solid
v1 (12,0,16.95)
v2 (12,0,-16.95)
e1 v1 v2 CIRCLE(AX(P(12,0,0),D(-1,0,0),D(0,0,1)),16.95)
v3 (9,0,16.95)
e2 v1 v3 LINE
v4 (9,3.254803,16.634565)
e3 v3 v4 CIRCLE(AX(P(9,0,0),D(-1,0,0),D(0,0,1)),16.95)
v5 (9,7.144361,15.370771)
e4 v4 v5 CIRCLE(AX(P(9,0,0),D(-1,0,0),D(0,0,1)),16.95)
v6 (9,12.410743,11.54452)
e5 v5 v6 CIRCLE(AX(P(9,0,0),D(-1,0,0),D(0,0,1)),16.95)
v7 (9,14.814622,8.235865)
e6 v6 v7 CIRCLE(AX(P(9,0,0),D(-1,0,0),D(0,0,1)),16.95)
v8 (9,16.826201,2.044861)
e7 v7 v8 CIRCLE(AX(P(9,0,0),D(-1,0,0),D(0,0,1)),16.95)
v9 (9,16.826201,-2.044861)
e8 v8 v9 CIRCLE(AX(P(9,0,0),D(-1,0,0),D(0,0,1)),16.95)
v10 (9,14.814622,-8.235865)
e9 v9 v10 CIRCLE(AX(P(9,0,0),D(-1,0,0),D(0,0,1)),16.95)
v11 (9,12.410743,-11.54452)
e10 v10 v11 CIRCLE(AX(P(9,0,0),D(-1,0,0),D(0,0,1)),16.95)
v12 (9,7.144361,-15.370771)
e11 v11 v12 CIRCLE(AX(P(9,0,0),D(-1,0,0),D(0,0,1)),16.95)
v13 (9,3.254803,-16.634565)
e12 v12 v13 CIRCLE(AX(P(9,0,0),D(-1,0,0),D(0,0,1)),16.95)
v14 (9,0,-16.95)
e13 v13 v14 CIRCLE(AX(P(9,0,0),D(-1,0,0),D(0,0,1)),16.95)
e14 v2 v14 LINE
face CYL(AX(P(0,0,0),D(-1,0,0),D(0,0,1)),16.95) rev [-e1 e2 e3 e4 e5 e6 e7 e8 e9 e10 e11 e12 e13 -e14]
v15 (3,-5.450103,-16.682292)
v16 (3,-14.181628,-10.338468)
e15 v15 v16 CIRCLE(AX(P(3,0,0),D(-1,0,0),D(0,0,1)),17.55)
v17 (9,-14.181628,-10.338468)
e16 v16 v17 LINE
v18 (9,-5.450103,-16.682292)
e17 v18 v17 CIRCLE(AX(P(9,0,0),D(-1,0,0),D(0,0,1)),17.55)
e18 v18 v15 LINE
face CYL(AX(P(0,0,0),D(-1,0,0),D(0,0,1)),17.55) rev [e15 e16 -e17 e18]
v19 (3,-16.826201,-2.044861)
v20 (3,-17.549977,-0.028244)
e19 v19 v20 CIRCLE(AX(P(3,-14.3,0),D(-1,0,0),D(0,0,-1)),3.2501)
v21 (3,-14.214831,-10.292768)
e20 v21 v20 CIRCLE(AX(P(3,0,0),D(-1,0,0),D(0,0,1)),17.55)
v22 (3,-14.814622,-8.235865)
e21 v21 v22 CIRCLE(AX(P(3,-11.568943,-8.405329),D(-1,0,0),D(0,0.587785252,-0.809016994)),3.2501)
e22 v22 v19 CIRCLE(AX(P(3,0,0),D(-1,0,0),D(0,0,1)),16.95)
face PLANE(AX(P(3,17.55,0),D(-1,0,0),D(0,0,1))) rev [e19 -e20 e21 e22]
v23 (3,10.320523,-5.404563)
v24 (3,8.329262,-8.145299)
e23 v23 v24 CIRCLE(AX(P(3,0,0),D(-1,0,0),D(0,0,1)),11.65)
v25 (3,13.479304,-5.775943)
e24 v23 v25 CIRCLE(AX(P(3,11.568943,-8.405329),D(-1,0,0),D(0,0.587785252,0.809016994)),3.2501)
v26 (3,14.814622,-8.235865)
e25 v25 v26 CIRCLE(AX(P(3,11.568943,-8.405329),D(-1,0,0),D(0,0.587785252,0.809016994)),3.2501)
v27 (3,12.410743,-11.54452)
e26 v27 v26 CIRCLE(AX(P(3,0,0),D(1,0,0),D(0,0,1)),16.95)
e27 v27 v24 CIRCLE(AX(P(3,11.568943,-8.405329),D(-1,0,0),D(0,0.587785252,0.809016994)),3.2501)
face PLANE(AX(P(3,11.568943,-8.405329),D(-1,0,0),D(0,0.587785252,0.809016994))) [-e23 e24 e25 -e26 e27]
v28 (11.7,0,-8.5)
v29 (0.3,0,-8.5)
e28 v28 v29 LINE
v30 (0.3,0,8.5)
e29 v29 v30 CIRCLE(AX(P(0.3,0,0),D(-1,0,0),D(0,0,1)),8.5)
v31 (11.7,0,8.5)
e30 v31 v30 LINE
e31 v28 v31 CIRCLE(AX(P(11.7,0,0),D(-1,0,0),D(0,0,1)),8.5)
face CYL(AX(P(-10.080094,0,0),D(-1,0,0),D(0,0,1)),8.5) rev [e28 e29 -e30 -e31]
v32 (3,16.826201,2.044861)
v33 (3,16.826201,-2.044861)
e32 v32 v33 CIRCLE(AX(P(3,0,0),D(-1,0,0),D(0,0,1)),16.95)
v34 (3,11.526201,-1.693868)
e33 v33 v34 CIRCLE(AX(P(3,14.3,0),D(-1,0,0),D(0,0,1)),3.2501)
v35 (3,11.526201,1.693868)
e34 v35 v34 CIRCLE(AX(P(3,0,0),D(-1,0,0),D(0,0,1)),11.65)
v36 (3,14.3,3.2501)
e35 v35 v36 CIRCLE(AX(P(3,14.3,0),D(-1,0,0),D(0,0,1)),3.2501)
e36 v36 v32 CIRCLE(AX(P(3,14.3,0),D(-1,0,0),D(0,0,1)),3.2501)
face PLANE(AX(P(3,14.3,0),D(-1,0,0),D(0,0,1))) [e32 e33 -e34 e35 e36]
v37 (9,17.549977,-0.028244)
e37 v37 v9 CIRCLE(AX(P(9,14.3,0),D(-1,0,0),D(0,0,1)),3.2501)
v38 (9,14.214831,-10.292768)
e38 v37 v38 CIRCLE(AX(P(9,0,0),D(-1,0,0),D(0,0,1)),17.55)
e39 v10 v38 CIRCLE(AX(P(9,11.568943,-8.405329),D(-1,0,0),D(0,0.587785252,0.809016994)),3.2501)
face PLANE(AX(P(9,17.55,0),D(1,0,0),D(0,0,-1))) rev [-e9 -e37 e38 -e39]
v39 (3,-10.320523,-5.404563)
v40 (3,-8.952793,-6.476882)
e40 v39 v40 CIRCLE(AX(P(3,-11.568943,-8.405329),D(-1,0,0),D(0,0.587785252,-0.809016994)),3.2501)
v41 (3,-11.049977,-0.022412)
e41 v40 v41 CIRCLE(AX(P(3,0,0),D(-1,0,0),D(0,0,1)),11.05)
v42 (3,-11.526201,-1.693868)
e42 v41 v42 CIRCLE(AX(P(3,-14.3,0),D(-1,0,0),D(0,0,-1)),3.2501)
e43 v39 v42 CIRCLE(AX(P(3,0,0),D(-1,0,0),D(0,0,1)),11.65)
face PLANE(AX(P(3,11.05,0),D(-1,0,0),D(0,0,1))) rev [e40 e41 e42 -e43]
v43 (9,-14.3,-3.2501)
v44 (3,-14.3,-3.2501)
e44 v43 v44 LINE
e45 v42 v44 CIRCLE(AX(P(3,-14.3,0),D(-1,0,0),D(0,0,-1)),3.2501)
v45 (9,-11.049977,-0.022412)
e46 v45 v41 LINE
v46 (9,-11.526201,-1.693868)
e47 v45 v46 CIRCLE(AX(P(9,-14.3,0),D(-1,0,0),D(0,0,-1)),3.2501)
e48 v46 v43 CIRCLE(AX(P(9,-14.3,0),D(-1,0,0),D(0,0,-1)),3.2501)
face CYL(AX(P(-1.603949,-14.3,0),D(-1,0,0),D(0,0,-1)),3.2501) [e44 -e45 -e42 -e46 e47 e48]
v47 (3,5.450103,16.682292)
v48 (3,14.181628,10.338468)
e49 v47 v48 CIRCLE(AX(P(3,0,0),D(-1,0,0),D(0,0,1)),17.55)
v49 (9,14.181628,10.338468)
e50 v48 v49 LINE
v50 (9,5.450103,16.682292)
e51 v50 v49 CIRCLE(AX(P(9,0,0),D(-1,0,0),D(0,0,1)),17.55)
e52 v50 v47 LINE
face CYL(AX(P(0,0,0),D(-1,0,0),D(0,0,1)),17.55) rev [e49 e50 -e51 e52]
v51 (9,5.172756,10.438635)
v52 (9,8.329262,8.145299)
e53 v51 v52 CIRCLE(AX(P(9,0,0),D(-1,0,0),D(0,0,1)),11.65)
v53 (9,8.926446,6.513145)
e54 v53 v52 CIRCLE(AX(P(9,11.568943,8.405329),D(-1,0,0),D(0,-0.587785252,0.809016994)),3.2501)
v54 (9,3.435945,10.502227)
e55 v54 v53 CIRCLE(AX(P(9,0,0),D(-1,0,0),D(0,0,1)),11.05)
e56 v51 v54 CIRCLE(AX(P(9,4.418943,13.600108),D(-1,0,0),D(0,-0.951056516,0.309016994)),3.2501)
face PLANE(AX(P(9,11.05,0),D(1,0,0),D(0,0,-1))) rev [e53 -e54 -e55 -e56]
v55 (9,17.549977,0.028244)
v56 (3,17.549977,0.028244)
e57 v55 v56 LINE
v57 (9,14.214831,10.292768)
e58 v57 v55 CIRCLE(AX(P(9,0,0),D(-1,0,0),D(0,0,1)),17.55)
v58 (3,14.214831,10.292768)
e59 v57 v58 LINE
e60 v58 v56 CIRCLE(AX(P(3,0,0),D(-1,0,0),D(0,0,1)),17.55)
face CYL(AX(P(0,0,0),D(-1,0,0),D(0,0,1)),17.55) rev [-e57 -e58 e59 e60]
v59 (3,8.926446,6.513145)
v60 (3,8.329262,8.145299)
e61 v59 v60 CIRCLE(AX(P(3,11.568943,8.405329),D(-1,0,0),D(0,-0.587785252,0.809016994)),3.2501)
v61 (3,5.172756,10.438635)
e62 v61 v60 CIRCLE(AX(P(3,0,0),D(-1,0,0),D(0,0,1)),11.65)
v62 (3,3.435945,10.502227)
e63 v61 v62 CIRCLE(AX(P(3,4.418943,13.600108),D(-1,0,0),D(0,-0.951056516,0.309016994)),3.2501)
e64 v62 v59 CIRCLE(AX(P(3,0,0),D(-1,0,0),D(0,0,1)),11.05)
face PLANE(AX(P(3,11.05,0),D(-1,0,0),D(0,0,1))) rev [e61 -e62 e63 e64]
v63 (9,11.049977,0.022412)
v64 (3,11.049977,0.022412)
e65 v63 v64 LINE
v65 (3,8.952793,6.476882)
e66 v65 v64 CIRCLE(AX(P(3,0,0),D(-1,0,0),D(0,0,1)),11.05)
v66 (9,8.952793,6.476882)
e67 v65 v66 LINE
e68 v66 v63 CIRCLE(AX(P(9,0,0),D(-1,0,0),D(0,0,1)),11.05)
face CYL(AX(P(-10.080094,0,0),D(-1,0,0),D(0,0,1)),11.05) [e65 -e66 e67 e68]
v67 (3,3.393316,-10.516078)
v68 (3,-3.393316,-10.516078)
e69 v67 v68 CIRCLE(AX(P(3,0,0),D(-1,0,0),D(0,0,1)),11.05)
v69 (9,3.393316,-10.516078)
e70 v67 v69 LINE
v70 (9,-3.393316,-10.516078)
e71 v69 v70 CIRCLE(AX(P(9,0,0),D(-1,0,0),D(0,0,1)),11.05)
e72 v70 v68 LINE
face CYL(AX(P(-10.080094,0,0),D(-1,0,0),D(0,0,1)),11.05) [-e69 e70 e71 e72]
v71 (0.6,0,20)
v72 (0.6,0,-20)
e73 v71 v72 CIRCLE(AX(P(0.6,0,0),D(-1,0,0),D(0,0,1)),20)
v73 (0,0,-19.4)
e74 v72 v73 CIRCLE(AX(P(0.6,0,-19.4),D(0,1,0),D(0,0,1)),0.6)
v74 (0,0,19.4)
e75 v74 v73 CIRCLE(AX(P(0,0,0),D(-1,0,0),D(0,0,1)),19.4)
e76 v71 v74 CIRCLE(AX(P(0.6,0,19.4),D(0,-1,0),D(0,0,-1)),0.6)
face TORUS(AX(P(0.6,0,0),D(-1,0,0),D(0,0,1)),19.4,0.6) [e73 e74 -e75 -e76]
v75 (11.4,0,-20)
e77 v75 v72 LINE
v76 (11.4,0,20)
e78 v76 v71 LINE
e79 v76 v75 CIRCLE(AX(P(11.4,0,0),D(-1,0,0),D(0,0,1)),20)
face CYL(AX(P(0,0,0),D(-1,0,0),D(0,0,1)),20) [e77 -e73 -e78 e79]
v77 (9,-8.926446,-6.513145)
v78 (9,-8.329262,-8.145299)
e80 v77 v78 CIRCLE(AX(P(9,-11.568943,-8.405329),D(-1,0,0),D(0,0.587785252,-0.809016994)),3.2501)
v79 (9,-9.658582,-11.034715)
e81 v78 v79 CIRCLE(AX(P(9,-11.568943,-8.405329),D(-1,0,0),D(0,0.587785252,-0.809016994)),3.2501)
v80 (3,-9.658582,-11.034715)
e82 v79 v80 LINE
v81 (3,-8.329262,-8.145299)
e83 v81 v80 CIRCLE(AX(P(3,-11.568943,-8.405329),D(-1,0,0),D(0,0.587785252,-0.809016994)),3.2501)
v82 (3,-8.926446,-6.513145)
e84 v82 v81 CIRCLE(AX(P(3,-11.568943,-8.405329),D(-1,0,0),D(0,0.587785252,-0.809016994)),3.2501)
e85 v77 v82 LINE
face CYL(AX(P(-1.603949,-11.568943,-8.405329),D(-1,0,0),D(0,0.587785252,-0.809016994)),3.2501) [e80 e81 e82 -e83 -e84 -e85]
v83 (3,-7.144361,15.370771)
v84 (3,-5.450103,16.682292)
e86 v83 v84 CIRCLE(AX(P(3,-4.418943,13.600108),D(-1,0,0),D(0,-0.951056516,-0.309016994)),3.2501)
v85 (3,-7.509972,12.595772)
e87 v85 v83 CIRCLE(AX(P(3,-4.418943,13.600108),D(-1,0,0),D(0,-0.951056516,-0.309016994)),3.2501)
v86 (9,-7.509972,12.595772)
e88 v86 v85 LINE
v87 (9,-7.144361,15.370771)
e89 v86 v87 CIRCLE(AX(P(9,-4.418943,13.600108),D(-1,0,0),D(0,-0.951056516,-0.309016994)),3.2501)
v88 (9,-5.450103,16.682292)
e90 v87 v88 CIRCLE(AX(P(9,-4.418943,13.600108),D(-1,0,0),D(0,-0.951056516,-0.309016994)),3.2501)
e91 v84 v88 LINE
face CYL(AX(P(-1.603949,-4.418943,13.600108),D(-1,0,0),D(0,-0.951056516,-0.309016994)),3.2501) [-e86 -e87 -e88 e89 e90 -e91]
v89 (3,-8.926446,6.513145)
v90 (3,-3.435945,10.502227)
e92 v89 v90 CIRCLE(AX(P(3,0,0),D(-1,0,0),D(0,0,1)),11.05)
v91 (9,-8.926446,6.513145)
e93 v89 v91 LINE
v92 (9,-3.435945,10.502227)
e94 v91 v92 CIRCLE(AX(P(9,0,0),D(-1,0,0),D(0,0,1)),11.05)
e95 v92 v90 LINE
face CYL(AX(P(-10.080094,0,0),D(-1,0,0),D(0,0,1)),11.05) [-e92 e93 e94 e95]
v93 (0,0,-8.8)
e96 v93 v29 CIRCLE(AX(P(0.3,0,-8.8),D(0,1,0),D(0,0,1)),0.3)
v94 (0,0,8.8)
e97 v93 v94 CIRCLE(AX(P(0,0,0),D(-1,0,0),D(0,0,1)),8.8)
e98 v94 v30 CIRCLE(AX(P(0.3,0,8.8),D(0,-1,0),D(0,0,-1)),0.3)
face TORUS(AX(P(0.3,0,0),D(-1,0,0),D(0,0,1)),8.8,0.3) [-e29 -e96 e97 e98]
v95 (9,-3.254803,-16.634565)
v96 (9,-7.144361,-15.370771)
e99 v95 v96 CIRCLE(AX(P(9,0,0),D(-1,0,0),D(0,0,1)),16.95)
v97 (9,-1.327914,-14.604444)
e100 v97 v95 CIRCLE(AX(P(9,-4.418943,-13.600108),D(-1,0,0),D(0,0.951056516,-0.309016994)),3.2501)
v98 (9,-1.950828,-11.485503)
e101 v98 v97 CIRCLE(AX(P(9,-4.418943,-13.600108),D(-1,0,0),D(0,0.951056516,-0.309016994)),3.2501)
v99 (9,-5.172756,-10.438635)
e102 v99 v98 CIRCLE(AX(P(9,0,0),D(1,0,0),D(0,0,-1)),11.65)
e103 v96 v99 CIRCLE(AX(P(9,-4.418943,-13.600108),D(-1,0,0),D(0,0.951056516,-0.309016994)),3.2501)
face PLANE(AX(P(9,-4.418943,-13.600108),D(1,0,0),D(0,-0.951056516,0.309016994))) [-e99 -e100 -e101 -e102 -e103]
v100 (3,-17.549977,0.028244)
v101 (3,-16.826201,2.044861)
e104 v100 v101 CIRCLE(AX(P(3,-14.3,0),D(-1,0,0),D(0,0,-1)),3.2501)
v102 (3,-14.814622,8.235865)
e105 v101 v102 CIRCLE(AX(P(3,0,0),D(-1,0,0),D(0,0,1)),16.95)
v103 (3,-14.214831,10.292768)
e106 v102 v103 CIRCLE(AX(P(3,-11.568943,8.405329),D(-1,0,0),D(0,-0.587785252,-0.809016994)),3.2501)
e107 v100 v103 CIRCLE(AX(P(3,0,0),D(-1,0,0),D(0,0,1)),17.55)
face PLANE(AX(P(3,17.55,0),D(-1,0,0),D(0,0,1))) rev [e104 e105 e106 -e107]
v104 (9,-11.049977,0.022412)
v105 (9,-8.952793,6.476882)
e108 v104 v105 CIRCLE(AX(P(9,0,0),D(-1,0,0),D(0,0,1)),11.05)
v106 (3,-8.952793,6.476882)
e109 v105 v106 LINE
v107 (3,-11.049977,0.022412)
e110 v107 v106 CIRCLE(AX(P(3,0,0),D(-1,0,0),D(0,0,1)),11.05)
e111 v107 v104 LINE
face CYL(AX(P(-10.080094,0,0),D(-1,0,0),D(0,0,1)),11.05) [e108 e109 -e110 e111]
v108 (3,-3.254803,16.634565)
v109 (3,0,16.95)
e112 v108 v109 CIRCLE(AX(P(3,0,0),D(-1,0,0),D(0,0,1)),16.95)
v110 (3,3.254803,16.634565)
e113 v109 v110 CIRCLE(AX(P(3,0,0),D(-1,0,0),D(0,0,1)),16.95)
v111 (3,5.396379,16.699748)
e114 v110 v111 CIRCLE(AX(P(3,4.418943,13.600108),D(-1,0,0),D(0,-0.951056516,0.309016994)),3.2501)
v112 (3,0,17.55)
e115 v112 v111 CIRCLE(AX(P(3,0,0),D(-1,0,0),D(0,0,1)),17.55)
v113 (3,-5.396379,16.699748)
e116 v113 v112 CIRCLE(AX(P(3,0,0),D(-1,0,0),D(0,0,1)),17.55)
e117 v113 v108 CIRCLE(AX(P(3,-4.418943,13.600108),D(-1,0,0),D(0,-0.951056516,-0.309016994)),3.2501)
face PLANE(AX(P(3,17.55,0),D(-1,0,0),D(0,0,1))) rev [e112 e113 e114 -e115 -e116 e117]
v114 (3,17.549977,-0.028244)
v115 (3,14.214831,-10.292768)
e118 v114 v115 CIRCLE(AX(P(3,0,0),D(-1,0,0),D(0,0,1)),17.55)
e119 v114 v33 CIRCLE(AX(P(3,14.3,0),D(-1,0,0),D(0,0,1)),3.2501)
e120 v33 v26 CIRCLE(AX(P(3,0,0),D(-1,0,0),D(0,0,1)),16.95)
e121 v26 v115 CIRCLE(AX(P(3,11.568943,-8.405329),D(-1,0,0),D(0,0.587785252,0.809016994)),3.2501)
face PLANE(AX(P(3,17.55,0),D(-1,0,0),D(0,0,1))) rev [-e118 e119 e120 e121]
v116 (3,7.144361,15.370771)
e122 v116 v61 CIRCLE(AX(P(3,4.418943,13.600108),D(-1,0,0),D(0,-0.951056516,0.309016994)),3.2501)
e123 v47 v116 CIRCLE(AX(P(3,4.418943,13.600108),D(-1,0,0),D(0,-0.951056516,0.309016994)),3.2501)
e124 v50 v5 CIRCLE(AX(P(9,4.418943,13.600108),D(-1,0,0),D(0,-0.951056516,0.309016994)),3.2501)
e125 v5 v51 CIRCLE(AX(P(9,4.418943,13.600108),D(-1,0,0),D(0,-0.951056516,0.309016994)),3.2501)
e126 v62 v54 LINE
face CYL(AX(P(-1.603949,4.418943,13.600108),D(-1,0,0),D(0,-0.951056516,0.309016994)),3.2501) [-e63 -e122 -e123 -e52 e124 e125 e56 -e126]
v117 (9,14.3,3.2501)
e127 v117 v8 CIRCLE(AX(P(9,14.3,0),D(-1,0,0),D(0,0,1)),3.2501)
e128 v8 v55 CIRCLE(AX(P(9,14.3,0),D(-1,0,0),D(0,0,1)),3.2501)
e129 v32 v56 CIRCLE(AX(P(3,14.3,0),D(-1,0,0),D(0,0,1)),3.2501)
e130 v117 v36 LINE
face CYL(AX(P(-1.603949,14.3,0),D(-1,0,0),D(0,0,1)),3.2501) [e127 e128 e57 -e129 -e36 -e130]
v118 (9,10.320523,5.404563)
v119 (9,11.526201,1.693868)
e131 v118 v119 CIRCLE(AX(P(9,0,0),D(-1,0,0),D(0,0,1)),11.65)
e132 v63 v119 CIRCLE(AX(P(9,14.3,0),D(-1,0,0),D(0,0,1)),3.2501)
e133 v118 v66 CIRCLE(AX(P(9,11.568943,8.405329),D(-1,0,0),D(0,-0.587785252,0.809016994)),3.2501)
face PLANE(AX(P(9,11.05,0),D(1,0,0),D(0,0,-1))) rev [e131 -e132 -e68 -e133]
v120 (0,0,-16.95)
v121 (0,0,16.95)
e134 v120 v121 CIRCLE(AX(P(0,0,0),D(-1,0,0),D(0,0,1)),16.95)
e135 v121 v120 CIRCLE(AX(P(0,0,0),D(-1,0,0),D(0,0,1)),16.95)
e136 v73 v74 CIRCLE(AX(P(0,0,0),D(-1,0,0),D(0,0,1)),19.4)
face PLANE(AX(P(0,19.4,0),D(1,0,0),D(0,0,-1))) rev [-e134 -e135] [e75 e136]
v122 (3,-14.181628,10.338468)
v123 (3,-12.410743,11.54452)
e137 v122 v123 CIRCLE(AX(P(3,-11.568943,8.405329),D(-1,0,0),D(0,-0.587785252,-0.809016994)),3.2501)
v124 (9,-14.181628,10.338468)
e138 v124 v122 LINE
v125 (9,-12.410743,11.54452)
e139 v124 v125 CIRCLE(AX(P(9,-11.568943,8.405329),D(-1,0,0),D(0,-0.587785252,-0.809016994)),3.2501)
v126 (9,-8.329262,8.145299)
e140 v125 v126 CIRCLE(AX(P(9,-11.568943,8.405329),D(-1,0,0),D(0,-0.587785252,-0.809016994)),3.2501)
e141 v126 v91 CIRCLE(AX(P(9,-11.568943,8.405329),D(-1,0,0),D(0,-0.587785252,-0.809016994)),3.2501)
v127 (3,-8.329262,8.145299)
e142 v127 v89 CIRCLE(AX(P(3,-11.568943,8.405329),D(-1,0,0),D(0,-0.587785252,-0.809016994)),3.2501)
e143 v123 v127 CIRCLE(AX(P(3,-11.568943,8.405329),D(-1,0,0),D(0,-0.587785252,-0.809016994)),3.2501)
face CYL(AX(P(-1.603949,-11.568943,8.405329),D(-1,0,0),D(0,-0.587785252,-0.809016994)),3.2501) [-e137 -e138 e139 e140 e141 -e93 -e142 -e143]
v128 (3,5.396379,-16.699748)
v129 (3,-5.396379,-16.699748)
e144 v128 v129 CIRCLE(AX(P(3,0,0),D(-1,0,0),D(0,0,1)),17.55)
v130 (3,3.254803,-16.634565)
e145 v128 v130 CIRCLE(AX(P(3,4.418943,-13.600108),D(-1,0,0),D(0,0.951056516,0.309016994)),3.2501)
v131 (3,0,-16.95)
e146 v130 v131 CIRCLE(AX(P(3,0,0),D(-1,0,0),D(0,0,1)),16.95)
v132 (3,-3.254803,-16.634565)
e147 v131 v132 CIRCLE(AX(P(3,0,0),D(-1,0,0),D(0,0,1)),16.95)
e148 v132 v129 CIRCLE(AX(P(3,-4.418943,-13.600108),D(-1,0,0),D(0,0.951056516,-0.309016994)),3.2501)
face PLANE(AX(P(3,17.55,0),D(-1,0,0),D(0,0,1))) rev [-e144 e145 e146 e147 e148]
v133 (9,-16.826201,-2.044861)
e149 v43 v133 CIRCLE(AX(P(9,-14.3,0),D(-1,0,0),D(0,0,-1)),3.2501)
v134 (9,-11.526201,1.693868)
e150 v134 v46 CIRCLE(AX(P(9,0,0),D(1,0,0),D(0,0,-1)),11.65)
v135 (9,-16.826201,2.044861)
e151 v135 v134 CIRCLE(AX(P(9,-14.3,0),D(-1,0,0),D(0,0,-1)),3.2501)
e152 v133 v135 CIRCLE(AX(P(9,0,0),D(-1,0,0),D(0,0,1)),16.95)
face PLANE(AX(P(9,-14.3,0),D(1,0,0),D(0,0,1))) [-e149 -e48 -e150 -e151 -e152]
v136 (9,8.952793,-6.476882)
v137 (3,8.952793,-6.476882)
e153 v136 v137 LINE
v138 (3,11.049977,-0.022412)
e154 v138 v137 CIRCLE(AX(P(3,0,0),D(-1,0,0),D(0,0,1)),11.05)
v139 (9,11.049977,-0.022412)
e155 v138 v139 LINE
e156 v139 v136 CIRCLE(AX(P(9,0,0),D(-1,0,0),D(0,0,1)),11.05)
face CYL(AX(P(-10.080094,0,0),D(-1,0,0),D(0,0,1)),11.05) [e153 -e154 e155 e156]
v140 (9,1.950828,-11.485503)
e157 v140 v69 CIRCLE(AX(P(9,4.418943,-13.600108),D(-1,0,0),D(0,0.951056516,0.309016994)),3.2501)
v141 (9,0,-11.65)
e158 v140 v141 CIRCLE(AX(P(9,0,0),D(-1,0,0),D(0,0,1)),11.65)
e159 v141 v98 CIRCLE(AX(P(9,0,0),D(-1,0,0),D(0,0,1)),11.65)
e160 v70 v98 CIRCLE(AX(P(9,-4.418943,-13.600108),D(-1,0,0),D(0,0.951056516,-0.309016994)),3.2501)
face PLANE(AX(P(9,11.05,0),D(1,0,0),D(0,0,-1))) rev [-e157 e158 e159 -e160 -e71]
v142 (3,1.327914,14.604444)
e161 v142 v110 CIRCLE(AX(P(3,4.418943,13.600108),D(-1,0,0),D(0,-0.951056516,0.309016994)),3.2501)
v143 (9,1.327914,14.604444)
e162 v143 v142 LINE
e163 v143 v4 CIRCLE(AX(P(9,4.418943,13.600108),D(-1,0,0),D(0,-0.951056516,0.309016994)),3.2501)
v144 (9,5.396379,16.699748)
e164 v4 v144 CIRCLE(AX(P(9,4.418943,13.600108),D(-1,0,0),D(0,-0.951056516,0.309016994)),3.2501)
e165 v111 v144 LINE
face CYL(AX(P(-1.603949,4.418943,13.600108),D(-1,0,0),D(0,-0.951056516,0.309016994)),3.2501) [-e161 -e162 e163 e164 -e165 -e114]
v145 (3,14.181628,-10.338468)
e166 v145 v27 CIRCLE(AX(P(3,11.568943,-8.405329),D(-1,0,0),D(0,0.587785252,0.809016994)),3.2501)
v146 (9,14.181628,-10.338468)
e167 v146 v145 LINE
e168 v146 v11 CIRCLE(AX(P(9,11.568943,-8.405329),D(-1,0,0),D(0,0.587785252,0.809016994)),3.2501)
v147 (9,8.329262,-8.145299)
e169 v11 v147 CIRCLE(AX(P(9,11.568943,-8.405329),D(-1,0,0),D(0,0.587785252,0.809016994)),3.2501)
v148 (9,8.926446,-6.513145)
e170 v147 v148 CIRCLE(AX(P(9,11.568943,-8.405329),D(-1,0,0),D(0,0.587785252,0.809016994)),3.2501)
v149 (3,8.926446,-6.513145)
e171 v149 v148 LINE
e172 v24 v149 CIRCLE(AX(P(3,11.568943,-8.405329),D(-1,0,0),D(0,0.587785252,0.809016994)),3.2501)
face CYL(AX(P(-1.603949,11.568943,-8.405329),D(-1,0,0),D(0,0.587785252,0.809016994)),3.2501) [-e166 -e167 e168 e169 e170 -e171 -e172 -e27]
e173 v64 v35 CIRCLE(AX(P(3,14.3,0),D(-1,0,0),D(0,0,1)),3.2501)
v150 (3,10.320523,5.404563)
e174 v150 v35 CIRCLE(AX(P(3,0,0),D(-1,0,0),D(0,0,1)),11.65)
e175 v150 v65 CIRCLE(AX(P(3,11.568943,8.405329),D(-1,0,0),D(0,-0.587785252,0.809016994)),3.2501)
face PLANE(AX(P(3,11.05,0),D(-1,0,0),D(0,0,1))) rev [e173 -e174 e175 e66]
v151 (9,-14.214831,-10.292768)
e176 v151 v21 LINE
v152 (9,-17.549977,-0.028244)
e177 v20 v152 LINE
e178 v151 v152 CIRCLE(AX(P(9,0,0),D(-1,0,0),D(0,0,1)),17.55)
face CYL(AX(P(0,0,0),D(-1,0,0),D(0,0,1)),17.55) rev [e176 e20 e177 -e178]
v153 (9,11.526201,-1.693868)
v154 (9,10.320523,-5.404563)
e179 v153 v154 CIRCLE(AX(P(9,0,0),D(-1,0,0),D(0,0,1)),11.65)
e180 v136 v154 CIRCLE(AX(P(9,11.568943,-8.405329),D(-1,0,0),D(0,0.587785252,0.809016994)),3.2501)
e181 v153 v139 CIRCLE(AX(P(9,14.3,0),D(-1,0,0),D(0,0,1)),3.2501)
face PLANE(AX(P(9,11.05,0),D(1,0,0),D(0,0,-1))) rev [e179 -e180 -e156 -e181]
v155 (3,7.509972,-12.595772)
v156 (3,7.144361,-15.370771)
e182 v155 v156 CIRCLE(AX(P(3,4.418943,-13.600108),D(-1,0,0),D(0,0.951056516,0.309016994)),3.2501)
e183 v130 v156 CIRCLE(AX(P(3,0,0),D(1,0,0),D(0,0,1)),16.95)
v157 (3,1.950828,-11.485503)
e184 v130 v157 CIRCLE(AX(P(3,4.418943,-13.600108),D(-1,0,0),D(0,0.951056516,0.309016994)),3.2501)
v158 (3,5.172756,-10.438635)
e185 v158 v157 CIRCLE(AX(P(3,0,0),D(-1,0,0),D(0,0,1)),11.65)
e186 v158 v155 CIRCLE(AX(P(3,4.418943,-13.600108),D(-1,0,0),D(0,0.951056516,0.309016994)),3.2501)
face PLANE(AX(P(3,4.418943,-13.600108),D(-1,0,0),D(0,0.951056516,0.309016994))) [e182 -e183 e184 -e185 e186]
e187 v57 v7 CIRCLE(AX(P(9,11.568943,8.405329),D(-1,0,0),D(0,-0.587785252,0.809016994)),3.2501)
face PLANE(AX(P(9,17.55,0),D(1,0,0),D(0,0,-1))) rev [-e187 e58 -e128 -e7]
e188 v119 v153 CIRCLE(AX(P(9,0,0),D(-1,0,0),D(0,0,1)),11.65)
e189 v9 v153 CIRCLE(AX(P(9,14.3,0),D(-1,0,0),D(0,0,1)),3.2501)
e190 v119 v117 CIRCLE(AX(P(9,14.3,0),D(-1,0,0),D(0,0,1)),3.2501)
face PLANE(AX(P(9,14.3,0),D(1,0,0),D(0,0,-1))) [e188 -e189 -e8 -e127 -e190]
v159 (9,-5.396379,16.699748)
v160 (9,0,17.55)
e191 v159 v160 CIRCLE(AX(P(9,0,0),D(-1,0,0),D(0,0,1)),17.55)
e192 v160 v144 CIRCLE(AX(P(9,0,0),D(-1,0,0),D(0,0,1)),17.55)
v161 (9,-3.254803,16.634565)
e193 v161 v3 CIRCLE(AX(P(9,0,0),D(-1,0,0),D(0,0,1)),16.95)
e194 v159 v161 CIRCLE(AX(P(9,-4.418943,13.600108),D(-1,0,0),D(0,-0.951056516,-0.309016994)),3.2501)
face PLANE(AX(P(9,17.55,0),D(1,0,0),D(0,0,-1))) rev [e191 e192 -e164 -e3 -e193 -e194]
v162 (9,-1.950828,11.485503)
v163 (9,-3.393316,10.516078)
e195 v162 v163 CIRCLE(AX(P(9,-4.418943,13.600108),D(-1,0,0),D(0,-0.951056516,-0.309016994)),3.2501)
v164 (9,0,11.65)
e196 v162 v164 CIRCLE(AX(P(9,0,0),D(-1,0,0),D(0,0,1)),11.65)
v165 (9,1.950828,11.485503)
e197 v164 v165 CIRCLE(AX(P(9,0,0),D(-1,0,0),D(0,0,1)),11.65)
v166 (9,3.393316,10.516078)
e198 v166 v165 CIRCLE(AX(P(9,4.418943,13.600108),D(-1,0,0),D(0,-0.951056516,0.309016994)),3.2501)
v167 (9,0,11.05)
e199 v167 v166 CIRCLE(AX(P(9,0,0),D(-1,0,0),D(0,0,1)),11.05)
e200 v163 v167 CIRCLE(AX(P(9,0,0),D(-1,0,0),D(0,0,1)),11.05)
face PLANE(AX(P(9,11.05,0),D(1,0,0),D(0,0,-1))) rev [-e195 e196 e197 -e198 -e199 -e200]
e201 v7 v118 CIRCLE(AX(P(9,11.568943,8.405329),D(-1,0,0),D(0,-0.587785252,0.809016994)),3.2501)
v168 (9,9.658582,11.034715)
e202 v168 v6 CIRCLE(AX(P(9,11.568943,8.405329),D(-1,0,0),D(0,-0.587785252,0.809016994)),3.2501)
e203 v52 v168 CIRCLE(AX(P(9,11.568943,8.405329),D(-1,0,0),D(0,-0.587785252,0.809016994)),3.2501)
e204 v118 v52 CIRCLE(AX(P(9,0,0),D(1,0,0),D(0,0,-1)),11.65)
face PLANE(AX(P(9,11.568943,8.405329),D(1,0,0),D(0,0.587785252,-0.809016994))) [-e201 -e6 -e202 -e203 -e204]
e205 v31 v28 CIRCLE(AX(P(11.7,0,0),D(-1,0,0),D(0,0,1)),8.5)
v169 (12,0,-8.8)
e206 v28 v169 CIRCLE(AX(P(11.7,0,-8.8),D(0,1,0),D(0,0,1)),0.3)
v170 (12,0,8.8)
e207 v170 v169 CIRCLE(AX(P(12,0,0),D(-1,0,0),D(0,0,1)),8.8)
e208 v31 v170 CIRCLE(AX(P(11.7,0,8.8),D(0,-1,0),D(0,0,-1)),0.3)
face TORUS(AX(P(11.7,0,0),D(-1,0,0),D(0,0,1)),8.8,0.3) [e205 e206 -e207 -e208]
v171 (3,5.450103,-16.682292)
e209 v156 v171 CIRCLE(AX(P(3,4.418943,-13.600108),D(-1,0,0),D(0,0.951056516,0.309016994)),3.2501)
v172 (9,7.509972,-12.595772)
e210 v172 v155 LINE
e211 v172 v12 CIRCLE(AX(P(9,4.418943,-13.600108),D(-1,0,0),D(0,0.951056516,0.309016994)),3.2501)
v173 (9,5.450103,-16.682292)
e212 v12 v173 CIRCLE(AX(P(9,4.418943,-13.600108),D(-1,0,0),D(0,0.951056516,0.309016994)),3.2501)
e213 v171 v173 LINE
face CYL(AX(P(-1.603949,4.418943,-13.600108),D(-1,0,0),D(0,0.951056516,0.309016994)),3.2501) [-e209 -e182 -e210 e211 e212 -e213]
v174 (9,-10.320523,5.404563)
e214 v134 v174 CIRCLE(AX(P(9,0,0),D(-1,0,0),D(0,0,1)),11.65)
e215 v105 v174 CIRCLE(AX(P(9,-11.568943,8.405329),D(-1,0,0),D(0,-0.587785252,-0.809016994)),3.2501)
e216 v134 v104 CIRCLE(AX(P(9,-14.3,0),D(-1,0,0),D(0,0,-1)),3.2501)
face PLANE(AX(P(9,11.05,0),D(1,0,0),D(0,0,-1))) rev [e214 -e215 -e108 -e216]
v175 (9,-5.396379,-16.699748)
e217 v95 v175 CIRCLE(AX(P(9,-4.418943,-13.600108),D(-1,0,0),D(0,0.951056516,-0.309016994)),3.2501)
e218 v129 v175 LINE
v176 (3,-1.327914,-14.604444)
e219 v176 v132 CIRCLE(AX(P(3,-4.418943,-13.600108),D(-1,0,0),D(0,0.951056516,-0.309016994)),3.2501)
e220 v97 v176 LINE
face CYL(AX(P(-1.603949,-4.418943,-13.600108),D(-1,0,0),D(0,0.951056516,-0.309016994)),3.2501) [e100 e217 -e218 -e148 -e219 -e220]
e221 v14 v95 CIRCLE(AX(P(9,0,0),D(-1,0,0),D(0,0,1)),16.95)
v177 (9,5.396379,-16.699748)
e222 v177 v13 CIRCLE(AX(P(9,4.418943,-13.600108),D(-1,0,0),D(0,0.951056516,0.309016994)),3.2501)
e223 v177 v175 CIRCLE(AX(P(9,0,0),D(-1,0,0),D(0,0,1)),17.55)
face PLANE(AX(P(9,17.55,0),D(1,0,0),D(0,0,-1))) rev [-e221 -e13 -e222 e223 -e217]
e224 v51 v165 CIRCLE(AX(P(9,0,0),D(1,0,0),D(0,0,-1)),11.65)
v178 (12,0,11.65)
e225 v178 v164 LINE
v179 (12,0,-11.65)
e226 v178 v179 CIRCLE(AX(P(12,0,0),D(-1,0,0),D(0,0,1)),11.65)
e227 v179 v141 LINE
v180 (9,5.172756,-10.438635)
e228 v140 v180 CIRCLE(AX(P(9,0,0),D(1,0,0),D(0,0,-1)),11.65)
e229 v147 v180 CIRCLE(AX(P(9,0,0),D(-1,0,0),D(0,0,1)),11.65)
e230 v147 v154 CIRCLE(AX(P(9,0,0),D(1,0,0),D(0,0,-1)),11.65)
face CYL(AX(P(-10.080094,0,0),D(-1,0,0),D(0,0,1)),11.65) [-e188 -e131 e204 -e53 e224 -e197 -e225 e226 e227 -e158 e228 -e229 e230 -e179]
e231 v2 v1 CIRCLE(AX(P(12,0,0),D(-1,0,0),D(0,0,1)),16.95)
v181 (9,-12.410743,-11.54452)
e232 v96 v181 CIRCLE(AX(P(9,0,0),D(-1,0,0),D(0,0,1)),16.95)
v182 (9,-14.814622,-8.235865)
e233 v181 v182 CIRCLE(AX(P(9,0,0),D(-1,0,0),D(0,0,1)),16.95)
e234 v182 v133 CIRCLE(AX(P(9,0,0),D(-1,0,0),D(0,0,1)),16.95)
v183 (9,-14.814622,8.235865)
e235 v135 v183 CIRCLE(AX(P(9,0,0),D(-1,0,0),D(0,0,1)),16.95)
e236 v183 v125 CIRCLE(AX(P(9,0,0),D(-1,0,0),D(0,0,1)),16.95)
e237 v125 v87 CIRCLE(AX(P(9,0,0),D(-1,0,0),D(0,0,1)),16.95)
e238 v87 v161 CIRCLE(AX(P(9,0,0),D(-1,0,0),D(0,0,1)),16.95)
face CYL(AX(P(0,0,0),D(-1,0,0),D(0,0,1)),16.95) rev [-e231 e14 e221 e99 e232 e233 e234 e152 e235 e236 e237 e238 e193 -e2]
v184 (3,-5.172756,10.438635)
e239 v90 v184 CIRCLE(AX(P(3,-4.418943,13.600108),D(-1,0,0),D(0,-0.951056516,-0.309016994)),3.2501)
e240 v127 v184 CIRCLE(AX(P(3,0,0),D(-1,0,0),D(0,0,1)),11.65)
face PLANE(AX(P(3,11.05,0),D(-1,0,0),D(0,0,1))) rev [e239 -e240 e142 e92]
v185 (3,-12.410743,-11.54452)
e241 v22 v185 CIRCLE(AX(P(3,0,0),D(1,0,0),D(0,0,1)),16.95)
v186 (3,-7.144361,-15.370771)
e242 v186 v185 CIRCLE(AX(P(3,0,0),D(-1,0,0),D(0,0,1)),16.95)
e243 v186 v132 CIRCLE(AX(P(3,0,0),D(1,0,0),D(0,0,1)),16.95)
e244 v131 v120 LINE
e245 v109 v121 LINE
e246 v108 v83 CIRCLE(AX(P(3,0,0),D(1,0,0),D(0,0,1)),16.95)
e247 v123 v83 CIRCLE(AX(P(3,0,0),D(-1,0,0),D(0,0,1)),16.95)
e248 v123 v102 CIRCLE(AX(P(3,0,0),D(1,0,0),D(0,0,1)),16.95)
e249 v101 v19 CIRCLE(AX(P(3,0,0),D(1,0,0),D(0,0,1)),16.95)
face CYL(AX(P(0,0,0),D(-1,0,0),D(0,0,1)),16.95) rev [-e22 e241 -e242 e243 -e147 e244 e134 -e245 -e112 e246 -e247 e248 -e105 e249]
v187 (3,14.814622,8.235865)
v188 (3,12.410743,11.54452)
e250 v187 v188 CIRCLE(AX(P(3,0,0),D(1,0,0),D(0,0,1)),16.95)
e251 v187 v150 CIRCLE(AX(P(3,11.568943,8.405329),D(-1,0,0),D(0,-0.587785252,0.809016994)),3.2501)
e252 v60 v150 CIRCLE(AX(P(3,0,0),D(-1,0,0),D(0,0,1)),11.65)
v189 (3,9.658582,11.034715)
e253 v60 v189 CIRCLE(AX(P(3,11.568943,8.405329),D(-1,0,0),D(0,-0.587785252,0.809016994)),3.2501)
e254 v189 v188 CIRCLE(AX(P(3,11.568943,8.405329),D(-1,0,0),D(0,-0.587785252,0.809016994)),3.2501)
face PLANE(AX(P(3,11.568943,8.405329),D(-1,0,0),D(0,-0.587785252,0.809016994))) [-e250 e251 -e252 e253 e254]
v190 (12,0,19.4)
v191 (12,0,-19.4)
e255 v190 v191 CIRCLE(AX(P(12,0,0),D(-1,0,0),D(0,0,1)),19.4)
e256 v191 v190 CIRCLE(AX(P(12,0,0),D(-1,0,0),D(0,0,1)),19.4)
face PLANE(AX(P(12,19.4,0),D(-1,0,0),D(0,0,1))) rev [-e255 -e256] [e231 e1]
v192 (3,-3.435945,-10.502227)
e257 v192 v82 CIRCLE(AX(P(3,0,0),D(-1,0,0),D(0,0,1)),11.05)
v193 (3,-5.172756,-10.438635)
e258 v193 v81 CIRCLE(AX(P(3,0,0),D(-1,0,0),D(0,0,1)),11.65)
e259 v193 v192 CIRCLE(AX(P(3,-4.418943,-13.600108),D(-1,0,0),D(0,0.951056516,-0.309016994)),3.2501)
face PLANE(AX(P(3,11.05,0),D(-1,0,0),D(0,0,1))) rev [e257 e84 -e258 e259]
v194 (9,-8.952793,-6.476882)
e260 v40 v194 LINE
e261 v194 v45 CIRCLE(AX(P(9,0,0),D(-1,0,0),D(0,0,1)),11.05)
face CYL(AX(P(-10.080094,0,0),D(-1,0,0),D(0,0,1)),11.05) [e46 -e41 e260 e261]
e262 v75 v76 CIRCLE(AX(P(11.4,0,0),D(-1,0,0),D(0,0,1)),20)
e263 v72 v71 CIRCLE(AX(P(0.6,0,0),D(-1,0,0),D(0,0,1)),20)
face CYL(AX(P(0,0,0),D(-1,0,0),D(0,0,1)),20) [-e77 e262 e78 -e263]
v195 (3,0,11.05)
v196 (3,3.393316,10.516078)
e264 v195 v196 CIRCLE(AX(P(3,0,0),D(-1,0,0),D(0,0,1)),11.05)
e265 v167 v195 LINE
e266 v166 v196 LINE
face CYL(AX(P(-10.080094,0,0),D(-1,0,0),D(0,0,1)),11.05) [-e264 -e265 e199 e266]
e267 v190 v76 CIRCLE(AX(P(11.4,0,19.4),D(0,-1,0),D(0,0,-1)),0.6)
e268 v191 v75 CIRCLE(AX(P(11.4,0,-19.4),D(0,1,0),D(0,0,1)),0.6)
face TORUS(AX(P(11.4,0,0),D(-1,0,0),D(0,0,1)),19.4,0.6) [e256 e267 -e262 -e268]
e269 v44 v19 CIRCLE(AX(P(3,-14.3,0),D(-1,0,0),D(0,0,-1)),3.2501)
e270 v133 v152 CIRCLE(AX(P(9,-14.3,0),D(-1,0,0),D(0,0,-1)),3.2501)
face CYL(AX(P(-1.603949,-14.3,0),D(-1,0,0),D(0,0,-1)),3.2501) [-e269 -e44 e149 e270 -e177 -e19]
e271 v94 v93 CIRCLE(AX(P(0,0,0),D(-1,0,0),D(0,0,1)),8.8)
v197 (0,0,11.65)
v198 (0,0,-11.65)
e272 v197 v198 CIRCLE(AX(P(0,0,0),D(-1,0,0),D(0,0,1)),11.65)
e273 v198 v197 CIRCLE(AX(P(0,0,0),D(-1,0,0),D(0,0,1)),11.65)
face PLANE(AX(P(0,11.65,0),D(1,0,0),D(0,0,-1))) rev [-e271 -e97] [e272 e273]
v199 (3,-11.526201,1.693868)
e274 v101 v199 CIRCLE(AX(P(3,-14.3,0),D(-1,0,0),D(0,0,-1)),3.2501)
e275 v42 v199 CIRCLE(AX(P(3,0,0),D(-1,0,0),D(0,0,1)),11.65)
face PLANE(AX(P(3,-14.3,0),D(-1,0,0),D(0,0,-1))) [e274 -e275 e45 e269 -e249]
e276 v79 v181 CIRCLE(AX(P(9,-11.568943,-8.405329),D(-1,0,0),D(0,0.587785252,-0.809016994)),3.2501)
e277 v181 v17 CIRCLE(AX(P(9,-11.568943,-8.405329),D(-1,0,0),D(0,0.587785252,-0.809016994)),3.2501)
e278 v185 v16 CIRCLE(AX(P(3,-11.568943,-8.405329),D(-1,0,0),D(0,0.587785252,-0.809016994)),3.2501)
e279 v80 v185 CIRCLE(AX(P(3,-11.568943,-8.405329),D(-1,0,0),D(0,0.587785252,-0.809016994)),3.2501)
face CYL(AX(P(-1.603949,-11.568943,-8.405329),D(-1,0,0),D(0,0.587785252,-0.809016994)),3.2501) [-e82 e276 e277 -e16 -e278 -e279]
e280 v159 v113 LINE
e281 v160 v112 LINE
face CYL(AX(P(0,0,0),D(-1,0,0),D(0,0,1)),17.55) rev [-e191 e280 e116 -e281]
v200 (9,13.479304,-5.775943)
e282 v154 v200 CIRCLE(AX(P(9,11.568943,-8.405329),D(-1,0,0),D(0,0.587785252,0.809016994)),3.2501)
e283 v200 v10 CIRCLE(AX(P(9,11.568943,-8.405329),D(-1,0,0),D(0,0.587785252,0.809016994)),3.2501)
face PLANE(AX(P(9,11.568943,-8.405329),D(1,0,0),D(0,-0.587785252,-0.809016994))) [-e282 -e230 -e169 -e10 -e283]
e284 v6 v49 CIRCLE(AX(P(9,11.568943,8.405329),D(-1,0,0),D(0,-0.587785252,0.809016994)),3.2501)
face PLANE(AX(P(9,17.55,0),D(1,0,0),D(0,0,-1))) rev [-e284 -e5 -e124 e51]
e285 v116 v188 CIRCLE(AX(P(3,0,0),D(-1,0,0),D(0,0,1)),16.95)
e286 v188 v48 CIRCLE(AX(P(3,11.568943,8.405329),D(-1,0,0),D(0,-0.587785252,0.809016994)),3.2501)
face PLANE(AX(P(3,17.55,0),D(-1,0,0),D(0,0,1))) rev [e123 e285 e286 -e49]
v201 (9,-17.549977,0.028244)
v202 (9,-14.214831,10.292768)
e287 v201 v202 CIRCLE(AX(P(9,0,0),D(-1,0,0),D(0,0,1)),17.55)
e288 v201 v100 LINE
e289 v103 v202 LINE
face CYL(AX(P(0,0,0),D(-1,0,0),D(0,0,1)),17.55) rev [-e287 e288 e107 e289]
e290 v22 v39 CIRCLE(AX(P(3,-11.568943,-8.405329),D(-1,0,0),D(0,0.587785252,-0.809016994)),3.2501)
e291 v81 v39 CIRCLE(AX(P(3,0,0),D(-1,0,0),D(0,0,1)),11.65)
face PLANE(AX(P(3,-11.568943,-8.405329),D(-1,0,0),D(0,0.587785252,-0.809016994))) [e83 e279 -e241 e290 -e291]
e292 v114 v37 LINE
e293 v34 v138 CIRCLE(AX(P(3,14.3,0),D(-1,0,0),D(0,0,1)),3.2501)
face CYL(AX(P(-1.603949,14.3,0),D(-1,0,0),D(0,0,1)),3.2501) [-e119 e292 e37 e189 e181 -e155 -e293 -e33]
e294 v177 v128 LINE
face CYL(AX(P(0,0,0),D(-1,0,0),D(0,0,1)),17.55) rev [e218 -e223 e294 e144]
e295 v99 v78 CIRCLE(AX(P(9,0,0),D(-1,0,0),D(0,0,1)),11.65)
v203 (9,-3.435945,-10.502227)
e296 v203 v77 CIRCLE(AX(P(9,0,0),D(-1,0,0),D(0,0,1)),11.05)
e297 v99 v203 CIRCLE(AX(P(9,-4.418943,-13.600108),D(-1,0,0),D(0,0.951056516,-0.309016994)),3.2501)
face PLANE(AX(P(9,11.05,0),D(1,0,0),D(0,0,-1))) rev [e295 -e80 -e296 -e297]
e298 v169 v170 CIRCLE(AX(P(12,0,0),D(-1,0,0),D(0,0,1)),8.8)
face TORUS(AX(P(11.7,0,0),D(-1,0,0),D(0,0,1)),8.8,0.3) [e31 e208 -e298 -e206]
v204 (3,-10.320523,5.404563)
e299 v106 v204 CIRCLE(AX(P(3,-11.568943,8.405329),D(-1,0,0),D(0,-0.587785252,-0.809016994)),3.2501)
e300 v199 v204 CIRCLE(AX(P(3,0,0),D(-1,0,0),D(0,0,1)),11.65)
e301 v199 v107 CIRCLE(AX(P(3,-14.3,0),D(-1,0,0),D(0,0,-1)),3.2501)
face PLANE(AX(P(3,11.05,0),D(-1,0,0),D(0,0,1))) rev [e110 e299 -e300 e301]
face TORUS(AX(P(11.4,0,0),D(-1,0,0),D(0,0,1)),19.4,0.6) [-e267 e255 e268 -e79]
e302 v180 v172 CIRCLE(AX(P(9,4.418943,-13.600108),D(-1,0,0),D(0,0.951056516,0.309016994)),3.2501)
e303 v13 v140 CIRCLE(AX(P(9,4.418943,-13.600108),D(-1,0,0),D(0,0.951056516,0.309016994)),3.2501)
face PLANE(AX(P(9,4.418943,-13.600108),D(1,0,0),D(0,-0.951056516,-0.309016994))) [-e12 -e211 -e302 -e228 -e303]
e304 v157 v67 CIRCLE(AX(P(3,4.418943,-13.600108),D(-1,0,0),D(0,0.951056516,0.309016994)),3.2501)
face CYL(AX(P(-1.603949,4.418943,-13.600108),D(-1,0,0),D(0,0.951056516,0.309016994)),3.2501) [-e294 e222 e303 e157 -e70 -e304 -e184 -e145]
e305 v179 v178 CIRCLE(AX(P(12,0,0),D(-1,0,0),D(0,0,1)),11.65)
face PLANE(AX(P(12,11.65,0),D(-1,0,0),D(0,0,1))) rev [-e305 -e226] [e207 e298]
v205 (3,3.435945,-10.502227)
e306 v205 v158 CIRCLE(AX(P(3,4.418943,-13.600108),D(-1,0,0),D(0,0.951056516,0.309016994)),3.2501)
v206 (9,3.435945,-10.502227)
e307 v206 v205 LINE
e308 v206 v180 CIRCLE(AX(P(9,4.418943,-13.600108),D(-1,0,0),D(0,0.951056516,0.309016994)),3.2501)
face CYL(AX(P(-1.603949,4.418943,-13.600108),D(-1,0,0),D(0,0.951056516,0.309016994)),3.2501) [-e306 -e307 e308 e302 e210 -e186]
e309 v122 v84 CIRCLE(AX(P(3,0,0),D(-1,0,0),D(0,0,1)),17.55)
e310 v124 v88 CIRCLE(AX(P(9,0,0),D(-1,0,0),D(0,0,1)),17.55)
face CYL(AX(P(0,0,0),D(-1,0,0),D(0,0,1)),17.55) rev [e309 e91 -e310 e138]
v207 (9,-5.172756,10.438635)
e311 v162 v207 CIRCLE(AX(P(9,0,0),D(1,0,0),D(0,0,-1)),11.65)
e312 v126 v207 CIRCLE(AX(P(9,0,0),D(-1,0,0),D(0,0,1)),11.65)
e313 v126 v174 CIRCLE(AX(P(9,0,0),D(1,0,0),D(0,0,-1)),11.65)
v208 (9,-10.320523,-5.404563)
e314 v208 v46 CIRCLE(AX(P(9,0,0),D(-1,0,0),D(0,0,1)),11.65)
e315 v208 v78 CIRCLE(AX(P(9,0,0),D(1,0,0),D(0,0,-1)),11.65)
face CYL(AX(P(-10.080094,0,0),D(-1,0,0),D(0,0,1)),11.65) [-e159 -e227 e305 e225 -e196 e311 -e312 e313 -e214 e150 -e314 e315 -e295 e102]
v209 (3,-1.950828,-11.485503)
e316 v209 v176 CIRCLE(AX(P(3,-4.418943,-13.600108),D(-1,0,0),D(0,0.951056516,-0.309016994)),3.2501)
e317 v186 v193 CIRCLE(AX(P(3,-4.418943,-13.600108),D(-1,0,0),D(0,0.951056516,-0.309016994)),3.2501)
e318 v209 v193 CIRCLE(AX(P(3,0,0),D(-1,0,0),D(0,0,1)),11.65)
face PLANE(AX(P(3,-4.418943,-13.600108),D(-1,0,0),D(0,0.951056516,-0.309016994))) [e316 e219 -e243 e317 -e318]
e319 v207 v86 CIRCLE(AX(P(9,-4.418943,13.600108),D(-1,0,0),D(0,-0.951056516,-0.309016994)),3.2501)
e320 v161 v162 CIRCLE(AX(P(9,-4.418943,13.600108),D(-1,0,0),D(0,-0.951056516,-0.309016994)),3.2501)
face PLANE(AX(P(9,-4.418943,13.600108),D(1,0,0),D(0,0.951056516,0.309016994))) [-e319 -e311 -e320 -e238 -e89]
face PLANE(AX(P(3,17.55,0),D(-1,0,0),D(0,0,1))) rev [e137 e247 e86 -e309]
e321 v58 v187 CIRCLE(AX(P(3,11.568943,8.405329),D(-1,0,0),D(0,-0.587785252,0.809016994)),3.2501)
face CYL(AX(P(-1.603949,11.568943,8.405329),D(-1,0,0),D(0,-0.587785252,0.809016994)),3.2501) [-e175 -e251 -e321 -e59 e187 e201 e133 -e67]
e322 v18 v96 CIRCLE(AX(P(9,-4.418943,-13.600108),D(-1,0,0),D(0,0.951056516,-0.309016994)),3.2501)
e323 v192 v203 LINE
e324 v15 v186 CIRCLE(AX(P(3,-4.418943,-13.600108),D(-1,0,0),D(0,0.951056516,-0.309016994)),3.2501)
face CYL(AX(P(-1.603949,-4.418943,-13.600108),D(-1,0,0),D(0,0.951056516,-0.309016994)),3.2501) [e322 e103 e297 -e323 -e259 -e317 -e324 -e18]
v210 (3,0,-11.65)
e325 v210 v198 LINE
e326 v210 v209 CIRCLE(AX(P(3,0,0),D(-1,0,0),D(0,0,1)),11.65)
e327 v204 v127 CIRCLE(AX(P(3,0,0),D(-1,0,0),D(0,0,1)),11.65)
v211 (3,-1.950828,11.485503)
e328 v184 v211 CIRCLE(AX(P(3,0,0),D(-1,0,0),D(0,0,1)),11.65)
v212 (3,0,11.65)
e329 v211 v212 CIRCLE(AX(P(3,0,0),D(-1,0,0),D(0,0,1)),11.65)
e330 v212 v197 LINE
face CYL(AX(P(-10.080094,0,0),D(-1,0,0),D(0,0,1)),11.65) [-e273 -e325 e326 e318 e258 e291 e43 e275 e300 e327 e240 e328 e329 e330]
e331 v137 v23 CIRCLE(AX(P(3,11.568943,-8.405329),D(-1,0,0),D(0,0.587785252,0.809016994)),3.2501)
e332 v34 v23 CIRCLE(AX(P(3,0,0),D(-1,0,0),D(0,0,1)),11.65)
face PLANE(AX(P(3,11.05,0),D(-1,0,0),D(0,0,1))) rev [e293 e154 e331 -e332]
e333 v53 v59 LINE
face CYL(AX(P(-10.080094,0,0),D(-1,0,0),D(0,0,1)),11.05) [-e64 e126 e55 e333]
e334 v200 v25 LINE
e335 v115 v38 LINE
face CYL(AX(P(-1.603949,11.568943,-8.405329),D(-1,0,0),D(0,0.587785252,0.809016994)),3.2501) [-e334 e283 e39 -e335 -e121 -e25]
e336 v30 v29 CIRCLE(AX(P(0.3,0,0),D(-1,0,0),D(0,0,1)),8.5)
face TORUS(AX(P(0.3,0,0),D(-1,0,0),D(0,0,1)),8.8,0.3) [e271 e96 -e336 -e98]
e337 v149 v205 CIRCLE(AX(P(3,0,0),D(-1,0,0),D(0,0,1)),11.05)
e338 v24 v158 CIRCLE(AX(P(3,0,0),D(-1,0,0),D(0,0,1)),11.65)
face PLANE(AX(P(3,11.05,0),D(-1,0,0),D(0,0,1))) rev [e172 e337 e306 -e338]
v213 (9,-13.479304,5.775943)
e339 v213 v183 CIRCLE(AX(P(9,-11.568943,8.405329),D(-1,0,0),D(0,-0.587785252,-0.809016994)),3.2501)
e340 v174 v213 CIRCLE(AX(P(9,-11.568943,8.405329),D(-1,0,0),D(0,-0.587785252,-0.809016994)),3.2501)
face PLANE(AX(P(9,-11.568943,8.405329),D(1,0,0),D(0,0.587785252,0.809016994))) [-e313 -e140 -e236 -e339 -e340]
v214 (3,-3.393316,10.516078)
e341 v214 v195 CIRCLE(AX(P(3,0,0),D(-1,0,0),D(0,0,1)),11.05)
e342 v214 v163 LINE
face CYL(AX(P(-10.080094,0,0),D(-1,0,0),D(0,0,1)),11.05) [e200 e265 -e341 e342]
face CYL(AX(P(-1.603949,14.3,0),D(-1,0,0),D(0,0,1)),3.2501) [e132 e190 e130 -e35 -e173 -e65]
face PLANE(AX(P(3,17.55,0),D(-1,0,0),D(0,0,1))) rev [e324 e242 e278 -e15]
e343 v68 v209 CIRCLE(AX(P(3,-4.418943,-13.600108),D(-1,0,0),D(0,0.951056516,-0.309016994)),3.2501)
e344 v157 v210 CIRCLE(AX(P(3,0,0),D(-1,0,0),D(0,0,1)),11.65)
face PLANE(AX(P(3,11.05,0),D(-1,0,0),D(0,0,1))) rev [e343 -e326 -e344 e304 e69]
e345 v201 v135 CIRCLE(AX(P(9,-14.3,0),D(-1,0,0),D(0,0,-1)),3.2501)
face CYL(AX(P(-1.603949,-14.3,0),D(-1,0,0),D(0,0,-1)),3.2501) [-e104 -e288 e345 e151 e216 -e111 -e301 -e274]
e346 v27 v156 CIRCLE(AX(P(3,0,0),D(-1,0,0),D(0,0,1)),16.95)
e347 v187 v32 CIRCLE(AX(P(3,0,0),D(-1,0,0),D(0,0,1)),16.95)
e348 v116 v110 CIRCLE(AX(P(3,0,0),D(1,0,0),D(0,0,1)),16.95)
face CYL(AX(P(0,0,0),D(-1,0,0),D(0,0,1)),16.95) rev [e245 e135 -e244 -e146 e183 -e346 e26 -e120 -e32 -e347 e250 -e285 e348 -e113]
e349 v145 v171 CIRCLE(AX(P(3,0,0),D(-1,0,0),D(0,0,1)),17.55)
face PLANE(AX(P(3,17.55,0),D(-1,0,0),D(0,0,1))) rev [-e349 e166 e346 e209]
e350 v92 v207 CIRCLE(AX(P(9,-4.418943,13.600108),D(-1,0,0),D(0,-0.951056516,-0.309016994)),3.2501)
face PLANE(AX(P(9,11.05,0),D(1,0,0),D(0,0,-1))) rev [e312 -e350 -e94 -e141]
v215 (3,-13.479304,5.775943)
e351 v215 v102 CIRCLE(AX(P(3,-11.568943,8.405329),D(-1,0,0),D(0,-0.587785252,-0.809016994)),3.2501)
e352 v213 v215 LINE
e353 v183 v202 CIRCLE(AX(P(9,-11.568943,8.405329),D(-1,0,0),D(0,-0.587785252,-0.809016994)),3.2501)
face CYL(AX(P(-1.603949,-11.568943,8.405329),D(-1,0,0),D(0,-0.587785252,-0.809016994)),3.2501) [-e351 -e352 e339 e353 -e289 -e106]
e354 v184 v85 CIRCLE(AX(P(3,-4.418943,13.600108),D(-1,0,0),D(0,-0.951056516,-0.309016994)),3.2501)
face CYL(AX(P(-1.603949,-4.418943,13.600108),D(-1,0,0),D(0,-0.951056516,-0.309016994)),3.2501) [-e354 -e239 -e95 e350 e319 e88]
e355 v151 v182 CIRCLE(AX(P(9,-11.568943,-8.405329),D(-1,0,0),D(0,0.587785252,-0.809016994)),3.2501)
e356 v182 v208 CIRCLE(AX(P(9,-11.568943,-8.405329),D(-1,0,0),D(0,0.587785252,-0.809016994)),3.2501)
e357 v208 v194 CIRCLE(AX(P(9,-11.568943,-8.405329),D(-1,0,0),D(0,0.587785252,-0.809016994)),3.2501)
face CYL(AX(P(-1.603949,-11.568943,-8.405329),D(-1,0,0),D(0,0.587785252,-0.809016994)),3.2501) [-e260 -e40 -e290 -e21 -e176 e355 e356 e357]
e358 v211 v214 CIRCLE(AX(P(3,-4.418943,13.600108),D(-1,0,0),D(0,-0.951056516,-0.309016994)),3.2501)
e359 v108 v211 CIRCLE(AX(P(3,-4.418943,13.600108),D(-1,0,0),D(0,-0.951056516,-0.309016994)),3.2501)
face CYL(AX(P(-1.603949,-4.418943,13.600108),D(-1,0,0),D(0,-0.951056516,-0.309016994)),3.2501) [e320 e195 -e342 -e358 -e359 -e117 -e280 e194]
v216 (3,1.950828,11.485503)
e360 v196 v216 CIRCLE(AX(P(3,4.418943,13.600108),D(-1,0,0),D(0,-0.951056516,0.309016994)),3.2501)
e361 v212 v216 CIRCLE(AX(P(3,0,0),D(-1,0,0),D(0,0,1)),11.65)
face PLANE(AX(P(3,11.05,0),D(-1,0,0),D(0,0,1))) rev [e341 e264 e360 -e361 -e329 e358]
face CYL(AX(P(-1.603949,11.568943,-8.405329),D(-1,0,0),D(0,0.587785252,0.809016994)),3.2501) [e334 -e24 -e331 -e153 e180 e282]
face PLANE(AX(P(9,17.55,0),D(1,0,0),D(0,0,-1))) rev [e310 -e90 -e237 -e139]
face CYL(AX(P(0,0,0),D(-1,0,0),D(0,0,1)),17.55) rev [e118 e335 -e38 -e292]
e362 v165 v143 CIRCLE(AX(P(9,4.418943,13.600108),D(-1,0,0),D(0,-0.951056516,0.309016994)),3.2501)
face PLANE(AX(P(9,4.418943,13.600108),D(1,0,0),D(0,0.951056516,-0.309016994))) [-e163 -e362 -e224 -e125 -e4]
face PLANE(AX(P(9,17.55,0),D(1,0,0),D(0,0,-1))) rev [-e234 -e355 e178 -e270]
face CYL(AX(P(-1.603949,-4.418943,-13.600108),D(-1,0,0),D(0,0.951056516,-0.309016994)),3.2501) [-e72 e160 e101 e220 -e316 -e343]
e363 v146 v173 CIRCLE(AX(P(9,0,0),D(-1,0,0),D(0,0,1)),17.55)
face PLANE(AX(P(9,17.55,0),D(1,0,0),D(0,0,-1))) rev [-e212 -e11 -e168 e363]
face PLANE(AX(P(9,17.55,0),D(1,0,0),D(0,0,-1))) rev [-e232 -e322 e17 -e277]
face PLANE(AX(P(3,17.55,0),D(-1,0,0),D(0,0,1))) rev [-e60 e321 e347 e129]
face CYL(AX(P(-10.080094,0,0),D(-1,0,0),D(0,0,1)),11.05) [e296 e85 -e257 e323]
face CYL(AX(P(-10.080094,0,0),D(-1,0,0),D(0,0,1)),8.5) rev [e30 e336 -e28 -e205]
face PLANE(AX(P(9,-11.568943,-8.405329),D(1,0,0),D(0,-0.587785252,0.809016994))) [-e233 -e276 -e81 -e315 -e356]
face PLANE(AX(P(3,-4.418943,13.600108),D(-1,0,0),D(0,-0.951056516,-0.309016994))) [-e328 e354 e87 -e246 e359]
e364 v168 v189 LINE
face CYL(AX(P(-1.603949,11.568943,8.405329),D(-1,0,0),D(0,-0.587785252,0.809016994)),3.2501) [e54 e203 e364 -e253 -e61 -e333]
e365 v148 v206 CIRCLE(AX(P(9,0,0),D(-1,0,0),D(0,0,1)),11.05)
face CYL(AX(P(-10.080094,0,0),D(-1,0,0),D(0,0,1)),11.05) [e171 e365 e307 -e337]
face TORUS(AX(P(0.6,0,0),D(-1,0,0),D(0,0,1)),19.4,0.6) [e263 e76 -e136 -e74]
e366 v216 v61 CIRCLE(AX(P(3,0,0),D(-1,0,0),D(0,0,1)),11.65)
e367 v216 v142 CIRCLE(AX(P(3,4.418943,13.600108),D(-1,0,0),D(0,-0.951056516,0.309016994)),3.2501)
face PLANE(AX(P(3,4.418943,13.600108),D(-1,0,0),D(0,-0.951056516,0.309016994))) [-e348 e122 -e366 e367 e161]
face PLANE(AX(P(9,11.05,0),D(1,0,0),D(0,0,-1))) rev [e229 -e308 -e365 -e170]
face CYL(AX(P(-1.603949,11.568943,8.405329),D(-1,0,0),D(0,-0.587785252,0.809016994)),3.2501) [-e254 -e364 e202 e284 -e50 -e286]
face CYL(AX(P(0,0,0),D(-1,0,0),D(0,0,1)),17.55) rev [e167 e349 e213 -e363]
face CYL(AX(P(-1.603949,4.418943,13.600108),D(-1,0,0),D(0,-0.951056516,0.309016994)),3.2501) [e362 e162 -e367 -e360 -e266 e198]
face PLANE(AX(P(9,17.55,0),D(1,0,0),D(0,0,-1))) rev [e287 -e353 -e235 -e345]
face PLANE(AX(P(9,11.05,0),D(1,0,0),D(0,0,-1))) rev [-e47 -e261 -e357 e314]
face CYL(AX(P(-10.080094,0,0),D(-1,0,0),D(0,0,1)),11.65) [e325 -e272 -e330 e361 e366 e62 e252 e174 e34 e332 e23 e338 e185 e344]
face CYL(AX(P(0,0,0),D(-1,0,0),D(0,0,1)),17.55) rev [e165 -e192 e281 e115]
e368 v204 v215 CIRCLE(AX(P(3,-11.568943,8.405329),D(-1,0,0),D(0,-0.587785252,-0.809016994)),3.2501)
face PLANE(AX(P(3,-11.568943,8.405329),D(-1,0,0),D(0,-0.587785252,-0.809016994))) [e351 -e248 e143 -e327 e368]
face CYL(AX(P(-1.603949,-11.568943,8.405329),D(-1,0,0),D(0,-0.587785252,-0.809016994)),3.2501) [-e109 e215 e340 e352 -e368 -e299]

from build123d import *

# Parameters (mm, degrees)
SKETCH_3_W               = 6
SKETCH_3_H               = 3.2501
PATTERN_CIRCULAR_1_COUNT = 10


with BuildPart() as part:
    # 草图2 → Revolve 705 (revolve)
    with BuildSketch(Plane.XY, mode=Mode.PRIVATE) as revolve_705_sk:
        with BuildLine():
            Line((3, 11.05), (9, 11.05))
            Line((9, 11.05), (9, 11.65))
            Line((9, 11.65), (12, 11.65))
            Line((12, 11.65), (12, 8.8))
            ThreePointArc((12, 8.8), (11.912132034, 8.587867966), (11.7, 8.5))
            Line((11.7, 8.5), (0.3, 8.5))
            ThreePointArc((0.3, 8.5), (0.087867966, 8.587867966), (0, 8.8))
            Line((0, 8.8), (0, 11.65))
            Line((0, 11.65), (3, 11.65))
            Line((3, 11.65), (3, 11.05))
        make_face()
    revolve(revolve_705_sk.sketch.rotate(Axis((-10.080094127, 0, 0), (1, 0, 0)), 90), axis=Axis((-10.080094127, 0, 0), (1, 0, 0)))

    # 草图3 → 凸台-旋转1 (revolve)
    with BuildSketch(Plane.XY):
        with Locations((6, 12.67495)):
            Rectangle(SKETCH_3_W, SKETCH_3_H)
    revolve_1 = revolve(axis=Axis((-1.603948851, 14.3, 0), (1, 0, 0)))

    # 草图4 → 凸台-旋转2 (revolve)
    with BuildSketch(Plane.XY, mode=Mode.PRIVATE) as revolve_2_sk:
        with BuildLine():
            Line((9, 16.95), (12, 16.95))
            Line((12, 16.95), (12, 19.4))
            ThreePointArc((12, 19.4), (11.824264069, 19.824264069), (11.4, 20))
            Line((11.4, 20), (0.6, 20))
            ThreePointArc((0.6, 20), (0.175735931, 19.824264069), (0, 19.4))
            Line((0, 19.4), (0, 16.95))
            Line((0, 16.95), (3, 16.95))
            Line((3, 16.95), (3, 17.55))
            Line((3, 17.55), (9, 17.55))
            Line((9, 17.55), (9, 16.95))
        make_face()
    revolve(revolve_2_sk.sketch.rotate(Axis((0, 0, 0), (1, 0, 0)), 90), axis=Axis((0, 0, 0), (1, 0, 0)))

    # 阵列(圆周)1: 凸台-旋转1 ×10 about axis
    pattern_circular_1_axis = Axis((0, 0, 0), (1, 0, 0))
    for i in range(1, PATTERN_CIRCULAR_1_COUNT):
        add(revolve_1.rotate(pattern_circular_1_axis, i * 360 / PATTERN_CIRCULAR_1_COUNT))


solid = part.part
